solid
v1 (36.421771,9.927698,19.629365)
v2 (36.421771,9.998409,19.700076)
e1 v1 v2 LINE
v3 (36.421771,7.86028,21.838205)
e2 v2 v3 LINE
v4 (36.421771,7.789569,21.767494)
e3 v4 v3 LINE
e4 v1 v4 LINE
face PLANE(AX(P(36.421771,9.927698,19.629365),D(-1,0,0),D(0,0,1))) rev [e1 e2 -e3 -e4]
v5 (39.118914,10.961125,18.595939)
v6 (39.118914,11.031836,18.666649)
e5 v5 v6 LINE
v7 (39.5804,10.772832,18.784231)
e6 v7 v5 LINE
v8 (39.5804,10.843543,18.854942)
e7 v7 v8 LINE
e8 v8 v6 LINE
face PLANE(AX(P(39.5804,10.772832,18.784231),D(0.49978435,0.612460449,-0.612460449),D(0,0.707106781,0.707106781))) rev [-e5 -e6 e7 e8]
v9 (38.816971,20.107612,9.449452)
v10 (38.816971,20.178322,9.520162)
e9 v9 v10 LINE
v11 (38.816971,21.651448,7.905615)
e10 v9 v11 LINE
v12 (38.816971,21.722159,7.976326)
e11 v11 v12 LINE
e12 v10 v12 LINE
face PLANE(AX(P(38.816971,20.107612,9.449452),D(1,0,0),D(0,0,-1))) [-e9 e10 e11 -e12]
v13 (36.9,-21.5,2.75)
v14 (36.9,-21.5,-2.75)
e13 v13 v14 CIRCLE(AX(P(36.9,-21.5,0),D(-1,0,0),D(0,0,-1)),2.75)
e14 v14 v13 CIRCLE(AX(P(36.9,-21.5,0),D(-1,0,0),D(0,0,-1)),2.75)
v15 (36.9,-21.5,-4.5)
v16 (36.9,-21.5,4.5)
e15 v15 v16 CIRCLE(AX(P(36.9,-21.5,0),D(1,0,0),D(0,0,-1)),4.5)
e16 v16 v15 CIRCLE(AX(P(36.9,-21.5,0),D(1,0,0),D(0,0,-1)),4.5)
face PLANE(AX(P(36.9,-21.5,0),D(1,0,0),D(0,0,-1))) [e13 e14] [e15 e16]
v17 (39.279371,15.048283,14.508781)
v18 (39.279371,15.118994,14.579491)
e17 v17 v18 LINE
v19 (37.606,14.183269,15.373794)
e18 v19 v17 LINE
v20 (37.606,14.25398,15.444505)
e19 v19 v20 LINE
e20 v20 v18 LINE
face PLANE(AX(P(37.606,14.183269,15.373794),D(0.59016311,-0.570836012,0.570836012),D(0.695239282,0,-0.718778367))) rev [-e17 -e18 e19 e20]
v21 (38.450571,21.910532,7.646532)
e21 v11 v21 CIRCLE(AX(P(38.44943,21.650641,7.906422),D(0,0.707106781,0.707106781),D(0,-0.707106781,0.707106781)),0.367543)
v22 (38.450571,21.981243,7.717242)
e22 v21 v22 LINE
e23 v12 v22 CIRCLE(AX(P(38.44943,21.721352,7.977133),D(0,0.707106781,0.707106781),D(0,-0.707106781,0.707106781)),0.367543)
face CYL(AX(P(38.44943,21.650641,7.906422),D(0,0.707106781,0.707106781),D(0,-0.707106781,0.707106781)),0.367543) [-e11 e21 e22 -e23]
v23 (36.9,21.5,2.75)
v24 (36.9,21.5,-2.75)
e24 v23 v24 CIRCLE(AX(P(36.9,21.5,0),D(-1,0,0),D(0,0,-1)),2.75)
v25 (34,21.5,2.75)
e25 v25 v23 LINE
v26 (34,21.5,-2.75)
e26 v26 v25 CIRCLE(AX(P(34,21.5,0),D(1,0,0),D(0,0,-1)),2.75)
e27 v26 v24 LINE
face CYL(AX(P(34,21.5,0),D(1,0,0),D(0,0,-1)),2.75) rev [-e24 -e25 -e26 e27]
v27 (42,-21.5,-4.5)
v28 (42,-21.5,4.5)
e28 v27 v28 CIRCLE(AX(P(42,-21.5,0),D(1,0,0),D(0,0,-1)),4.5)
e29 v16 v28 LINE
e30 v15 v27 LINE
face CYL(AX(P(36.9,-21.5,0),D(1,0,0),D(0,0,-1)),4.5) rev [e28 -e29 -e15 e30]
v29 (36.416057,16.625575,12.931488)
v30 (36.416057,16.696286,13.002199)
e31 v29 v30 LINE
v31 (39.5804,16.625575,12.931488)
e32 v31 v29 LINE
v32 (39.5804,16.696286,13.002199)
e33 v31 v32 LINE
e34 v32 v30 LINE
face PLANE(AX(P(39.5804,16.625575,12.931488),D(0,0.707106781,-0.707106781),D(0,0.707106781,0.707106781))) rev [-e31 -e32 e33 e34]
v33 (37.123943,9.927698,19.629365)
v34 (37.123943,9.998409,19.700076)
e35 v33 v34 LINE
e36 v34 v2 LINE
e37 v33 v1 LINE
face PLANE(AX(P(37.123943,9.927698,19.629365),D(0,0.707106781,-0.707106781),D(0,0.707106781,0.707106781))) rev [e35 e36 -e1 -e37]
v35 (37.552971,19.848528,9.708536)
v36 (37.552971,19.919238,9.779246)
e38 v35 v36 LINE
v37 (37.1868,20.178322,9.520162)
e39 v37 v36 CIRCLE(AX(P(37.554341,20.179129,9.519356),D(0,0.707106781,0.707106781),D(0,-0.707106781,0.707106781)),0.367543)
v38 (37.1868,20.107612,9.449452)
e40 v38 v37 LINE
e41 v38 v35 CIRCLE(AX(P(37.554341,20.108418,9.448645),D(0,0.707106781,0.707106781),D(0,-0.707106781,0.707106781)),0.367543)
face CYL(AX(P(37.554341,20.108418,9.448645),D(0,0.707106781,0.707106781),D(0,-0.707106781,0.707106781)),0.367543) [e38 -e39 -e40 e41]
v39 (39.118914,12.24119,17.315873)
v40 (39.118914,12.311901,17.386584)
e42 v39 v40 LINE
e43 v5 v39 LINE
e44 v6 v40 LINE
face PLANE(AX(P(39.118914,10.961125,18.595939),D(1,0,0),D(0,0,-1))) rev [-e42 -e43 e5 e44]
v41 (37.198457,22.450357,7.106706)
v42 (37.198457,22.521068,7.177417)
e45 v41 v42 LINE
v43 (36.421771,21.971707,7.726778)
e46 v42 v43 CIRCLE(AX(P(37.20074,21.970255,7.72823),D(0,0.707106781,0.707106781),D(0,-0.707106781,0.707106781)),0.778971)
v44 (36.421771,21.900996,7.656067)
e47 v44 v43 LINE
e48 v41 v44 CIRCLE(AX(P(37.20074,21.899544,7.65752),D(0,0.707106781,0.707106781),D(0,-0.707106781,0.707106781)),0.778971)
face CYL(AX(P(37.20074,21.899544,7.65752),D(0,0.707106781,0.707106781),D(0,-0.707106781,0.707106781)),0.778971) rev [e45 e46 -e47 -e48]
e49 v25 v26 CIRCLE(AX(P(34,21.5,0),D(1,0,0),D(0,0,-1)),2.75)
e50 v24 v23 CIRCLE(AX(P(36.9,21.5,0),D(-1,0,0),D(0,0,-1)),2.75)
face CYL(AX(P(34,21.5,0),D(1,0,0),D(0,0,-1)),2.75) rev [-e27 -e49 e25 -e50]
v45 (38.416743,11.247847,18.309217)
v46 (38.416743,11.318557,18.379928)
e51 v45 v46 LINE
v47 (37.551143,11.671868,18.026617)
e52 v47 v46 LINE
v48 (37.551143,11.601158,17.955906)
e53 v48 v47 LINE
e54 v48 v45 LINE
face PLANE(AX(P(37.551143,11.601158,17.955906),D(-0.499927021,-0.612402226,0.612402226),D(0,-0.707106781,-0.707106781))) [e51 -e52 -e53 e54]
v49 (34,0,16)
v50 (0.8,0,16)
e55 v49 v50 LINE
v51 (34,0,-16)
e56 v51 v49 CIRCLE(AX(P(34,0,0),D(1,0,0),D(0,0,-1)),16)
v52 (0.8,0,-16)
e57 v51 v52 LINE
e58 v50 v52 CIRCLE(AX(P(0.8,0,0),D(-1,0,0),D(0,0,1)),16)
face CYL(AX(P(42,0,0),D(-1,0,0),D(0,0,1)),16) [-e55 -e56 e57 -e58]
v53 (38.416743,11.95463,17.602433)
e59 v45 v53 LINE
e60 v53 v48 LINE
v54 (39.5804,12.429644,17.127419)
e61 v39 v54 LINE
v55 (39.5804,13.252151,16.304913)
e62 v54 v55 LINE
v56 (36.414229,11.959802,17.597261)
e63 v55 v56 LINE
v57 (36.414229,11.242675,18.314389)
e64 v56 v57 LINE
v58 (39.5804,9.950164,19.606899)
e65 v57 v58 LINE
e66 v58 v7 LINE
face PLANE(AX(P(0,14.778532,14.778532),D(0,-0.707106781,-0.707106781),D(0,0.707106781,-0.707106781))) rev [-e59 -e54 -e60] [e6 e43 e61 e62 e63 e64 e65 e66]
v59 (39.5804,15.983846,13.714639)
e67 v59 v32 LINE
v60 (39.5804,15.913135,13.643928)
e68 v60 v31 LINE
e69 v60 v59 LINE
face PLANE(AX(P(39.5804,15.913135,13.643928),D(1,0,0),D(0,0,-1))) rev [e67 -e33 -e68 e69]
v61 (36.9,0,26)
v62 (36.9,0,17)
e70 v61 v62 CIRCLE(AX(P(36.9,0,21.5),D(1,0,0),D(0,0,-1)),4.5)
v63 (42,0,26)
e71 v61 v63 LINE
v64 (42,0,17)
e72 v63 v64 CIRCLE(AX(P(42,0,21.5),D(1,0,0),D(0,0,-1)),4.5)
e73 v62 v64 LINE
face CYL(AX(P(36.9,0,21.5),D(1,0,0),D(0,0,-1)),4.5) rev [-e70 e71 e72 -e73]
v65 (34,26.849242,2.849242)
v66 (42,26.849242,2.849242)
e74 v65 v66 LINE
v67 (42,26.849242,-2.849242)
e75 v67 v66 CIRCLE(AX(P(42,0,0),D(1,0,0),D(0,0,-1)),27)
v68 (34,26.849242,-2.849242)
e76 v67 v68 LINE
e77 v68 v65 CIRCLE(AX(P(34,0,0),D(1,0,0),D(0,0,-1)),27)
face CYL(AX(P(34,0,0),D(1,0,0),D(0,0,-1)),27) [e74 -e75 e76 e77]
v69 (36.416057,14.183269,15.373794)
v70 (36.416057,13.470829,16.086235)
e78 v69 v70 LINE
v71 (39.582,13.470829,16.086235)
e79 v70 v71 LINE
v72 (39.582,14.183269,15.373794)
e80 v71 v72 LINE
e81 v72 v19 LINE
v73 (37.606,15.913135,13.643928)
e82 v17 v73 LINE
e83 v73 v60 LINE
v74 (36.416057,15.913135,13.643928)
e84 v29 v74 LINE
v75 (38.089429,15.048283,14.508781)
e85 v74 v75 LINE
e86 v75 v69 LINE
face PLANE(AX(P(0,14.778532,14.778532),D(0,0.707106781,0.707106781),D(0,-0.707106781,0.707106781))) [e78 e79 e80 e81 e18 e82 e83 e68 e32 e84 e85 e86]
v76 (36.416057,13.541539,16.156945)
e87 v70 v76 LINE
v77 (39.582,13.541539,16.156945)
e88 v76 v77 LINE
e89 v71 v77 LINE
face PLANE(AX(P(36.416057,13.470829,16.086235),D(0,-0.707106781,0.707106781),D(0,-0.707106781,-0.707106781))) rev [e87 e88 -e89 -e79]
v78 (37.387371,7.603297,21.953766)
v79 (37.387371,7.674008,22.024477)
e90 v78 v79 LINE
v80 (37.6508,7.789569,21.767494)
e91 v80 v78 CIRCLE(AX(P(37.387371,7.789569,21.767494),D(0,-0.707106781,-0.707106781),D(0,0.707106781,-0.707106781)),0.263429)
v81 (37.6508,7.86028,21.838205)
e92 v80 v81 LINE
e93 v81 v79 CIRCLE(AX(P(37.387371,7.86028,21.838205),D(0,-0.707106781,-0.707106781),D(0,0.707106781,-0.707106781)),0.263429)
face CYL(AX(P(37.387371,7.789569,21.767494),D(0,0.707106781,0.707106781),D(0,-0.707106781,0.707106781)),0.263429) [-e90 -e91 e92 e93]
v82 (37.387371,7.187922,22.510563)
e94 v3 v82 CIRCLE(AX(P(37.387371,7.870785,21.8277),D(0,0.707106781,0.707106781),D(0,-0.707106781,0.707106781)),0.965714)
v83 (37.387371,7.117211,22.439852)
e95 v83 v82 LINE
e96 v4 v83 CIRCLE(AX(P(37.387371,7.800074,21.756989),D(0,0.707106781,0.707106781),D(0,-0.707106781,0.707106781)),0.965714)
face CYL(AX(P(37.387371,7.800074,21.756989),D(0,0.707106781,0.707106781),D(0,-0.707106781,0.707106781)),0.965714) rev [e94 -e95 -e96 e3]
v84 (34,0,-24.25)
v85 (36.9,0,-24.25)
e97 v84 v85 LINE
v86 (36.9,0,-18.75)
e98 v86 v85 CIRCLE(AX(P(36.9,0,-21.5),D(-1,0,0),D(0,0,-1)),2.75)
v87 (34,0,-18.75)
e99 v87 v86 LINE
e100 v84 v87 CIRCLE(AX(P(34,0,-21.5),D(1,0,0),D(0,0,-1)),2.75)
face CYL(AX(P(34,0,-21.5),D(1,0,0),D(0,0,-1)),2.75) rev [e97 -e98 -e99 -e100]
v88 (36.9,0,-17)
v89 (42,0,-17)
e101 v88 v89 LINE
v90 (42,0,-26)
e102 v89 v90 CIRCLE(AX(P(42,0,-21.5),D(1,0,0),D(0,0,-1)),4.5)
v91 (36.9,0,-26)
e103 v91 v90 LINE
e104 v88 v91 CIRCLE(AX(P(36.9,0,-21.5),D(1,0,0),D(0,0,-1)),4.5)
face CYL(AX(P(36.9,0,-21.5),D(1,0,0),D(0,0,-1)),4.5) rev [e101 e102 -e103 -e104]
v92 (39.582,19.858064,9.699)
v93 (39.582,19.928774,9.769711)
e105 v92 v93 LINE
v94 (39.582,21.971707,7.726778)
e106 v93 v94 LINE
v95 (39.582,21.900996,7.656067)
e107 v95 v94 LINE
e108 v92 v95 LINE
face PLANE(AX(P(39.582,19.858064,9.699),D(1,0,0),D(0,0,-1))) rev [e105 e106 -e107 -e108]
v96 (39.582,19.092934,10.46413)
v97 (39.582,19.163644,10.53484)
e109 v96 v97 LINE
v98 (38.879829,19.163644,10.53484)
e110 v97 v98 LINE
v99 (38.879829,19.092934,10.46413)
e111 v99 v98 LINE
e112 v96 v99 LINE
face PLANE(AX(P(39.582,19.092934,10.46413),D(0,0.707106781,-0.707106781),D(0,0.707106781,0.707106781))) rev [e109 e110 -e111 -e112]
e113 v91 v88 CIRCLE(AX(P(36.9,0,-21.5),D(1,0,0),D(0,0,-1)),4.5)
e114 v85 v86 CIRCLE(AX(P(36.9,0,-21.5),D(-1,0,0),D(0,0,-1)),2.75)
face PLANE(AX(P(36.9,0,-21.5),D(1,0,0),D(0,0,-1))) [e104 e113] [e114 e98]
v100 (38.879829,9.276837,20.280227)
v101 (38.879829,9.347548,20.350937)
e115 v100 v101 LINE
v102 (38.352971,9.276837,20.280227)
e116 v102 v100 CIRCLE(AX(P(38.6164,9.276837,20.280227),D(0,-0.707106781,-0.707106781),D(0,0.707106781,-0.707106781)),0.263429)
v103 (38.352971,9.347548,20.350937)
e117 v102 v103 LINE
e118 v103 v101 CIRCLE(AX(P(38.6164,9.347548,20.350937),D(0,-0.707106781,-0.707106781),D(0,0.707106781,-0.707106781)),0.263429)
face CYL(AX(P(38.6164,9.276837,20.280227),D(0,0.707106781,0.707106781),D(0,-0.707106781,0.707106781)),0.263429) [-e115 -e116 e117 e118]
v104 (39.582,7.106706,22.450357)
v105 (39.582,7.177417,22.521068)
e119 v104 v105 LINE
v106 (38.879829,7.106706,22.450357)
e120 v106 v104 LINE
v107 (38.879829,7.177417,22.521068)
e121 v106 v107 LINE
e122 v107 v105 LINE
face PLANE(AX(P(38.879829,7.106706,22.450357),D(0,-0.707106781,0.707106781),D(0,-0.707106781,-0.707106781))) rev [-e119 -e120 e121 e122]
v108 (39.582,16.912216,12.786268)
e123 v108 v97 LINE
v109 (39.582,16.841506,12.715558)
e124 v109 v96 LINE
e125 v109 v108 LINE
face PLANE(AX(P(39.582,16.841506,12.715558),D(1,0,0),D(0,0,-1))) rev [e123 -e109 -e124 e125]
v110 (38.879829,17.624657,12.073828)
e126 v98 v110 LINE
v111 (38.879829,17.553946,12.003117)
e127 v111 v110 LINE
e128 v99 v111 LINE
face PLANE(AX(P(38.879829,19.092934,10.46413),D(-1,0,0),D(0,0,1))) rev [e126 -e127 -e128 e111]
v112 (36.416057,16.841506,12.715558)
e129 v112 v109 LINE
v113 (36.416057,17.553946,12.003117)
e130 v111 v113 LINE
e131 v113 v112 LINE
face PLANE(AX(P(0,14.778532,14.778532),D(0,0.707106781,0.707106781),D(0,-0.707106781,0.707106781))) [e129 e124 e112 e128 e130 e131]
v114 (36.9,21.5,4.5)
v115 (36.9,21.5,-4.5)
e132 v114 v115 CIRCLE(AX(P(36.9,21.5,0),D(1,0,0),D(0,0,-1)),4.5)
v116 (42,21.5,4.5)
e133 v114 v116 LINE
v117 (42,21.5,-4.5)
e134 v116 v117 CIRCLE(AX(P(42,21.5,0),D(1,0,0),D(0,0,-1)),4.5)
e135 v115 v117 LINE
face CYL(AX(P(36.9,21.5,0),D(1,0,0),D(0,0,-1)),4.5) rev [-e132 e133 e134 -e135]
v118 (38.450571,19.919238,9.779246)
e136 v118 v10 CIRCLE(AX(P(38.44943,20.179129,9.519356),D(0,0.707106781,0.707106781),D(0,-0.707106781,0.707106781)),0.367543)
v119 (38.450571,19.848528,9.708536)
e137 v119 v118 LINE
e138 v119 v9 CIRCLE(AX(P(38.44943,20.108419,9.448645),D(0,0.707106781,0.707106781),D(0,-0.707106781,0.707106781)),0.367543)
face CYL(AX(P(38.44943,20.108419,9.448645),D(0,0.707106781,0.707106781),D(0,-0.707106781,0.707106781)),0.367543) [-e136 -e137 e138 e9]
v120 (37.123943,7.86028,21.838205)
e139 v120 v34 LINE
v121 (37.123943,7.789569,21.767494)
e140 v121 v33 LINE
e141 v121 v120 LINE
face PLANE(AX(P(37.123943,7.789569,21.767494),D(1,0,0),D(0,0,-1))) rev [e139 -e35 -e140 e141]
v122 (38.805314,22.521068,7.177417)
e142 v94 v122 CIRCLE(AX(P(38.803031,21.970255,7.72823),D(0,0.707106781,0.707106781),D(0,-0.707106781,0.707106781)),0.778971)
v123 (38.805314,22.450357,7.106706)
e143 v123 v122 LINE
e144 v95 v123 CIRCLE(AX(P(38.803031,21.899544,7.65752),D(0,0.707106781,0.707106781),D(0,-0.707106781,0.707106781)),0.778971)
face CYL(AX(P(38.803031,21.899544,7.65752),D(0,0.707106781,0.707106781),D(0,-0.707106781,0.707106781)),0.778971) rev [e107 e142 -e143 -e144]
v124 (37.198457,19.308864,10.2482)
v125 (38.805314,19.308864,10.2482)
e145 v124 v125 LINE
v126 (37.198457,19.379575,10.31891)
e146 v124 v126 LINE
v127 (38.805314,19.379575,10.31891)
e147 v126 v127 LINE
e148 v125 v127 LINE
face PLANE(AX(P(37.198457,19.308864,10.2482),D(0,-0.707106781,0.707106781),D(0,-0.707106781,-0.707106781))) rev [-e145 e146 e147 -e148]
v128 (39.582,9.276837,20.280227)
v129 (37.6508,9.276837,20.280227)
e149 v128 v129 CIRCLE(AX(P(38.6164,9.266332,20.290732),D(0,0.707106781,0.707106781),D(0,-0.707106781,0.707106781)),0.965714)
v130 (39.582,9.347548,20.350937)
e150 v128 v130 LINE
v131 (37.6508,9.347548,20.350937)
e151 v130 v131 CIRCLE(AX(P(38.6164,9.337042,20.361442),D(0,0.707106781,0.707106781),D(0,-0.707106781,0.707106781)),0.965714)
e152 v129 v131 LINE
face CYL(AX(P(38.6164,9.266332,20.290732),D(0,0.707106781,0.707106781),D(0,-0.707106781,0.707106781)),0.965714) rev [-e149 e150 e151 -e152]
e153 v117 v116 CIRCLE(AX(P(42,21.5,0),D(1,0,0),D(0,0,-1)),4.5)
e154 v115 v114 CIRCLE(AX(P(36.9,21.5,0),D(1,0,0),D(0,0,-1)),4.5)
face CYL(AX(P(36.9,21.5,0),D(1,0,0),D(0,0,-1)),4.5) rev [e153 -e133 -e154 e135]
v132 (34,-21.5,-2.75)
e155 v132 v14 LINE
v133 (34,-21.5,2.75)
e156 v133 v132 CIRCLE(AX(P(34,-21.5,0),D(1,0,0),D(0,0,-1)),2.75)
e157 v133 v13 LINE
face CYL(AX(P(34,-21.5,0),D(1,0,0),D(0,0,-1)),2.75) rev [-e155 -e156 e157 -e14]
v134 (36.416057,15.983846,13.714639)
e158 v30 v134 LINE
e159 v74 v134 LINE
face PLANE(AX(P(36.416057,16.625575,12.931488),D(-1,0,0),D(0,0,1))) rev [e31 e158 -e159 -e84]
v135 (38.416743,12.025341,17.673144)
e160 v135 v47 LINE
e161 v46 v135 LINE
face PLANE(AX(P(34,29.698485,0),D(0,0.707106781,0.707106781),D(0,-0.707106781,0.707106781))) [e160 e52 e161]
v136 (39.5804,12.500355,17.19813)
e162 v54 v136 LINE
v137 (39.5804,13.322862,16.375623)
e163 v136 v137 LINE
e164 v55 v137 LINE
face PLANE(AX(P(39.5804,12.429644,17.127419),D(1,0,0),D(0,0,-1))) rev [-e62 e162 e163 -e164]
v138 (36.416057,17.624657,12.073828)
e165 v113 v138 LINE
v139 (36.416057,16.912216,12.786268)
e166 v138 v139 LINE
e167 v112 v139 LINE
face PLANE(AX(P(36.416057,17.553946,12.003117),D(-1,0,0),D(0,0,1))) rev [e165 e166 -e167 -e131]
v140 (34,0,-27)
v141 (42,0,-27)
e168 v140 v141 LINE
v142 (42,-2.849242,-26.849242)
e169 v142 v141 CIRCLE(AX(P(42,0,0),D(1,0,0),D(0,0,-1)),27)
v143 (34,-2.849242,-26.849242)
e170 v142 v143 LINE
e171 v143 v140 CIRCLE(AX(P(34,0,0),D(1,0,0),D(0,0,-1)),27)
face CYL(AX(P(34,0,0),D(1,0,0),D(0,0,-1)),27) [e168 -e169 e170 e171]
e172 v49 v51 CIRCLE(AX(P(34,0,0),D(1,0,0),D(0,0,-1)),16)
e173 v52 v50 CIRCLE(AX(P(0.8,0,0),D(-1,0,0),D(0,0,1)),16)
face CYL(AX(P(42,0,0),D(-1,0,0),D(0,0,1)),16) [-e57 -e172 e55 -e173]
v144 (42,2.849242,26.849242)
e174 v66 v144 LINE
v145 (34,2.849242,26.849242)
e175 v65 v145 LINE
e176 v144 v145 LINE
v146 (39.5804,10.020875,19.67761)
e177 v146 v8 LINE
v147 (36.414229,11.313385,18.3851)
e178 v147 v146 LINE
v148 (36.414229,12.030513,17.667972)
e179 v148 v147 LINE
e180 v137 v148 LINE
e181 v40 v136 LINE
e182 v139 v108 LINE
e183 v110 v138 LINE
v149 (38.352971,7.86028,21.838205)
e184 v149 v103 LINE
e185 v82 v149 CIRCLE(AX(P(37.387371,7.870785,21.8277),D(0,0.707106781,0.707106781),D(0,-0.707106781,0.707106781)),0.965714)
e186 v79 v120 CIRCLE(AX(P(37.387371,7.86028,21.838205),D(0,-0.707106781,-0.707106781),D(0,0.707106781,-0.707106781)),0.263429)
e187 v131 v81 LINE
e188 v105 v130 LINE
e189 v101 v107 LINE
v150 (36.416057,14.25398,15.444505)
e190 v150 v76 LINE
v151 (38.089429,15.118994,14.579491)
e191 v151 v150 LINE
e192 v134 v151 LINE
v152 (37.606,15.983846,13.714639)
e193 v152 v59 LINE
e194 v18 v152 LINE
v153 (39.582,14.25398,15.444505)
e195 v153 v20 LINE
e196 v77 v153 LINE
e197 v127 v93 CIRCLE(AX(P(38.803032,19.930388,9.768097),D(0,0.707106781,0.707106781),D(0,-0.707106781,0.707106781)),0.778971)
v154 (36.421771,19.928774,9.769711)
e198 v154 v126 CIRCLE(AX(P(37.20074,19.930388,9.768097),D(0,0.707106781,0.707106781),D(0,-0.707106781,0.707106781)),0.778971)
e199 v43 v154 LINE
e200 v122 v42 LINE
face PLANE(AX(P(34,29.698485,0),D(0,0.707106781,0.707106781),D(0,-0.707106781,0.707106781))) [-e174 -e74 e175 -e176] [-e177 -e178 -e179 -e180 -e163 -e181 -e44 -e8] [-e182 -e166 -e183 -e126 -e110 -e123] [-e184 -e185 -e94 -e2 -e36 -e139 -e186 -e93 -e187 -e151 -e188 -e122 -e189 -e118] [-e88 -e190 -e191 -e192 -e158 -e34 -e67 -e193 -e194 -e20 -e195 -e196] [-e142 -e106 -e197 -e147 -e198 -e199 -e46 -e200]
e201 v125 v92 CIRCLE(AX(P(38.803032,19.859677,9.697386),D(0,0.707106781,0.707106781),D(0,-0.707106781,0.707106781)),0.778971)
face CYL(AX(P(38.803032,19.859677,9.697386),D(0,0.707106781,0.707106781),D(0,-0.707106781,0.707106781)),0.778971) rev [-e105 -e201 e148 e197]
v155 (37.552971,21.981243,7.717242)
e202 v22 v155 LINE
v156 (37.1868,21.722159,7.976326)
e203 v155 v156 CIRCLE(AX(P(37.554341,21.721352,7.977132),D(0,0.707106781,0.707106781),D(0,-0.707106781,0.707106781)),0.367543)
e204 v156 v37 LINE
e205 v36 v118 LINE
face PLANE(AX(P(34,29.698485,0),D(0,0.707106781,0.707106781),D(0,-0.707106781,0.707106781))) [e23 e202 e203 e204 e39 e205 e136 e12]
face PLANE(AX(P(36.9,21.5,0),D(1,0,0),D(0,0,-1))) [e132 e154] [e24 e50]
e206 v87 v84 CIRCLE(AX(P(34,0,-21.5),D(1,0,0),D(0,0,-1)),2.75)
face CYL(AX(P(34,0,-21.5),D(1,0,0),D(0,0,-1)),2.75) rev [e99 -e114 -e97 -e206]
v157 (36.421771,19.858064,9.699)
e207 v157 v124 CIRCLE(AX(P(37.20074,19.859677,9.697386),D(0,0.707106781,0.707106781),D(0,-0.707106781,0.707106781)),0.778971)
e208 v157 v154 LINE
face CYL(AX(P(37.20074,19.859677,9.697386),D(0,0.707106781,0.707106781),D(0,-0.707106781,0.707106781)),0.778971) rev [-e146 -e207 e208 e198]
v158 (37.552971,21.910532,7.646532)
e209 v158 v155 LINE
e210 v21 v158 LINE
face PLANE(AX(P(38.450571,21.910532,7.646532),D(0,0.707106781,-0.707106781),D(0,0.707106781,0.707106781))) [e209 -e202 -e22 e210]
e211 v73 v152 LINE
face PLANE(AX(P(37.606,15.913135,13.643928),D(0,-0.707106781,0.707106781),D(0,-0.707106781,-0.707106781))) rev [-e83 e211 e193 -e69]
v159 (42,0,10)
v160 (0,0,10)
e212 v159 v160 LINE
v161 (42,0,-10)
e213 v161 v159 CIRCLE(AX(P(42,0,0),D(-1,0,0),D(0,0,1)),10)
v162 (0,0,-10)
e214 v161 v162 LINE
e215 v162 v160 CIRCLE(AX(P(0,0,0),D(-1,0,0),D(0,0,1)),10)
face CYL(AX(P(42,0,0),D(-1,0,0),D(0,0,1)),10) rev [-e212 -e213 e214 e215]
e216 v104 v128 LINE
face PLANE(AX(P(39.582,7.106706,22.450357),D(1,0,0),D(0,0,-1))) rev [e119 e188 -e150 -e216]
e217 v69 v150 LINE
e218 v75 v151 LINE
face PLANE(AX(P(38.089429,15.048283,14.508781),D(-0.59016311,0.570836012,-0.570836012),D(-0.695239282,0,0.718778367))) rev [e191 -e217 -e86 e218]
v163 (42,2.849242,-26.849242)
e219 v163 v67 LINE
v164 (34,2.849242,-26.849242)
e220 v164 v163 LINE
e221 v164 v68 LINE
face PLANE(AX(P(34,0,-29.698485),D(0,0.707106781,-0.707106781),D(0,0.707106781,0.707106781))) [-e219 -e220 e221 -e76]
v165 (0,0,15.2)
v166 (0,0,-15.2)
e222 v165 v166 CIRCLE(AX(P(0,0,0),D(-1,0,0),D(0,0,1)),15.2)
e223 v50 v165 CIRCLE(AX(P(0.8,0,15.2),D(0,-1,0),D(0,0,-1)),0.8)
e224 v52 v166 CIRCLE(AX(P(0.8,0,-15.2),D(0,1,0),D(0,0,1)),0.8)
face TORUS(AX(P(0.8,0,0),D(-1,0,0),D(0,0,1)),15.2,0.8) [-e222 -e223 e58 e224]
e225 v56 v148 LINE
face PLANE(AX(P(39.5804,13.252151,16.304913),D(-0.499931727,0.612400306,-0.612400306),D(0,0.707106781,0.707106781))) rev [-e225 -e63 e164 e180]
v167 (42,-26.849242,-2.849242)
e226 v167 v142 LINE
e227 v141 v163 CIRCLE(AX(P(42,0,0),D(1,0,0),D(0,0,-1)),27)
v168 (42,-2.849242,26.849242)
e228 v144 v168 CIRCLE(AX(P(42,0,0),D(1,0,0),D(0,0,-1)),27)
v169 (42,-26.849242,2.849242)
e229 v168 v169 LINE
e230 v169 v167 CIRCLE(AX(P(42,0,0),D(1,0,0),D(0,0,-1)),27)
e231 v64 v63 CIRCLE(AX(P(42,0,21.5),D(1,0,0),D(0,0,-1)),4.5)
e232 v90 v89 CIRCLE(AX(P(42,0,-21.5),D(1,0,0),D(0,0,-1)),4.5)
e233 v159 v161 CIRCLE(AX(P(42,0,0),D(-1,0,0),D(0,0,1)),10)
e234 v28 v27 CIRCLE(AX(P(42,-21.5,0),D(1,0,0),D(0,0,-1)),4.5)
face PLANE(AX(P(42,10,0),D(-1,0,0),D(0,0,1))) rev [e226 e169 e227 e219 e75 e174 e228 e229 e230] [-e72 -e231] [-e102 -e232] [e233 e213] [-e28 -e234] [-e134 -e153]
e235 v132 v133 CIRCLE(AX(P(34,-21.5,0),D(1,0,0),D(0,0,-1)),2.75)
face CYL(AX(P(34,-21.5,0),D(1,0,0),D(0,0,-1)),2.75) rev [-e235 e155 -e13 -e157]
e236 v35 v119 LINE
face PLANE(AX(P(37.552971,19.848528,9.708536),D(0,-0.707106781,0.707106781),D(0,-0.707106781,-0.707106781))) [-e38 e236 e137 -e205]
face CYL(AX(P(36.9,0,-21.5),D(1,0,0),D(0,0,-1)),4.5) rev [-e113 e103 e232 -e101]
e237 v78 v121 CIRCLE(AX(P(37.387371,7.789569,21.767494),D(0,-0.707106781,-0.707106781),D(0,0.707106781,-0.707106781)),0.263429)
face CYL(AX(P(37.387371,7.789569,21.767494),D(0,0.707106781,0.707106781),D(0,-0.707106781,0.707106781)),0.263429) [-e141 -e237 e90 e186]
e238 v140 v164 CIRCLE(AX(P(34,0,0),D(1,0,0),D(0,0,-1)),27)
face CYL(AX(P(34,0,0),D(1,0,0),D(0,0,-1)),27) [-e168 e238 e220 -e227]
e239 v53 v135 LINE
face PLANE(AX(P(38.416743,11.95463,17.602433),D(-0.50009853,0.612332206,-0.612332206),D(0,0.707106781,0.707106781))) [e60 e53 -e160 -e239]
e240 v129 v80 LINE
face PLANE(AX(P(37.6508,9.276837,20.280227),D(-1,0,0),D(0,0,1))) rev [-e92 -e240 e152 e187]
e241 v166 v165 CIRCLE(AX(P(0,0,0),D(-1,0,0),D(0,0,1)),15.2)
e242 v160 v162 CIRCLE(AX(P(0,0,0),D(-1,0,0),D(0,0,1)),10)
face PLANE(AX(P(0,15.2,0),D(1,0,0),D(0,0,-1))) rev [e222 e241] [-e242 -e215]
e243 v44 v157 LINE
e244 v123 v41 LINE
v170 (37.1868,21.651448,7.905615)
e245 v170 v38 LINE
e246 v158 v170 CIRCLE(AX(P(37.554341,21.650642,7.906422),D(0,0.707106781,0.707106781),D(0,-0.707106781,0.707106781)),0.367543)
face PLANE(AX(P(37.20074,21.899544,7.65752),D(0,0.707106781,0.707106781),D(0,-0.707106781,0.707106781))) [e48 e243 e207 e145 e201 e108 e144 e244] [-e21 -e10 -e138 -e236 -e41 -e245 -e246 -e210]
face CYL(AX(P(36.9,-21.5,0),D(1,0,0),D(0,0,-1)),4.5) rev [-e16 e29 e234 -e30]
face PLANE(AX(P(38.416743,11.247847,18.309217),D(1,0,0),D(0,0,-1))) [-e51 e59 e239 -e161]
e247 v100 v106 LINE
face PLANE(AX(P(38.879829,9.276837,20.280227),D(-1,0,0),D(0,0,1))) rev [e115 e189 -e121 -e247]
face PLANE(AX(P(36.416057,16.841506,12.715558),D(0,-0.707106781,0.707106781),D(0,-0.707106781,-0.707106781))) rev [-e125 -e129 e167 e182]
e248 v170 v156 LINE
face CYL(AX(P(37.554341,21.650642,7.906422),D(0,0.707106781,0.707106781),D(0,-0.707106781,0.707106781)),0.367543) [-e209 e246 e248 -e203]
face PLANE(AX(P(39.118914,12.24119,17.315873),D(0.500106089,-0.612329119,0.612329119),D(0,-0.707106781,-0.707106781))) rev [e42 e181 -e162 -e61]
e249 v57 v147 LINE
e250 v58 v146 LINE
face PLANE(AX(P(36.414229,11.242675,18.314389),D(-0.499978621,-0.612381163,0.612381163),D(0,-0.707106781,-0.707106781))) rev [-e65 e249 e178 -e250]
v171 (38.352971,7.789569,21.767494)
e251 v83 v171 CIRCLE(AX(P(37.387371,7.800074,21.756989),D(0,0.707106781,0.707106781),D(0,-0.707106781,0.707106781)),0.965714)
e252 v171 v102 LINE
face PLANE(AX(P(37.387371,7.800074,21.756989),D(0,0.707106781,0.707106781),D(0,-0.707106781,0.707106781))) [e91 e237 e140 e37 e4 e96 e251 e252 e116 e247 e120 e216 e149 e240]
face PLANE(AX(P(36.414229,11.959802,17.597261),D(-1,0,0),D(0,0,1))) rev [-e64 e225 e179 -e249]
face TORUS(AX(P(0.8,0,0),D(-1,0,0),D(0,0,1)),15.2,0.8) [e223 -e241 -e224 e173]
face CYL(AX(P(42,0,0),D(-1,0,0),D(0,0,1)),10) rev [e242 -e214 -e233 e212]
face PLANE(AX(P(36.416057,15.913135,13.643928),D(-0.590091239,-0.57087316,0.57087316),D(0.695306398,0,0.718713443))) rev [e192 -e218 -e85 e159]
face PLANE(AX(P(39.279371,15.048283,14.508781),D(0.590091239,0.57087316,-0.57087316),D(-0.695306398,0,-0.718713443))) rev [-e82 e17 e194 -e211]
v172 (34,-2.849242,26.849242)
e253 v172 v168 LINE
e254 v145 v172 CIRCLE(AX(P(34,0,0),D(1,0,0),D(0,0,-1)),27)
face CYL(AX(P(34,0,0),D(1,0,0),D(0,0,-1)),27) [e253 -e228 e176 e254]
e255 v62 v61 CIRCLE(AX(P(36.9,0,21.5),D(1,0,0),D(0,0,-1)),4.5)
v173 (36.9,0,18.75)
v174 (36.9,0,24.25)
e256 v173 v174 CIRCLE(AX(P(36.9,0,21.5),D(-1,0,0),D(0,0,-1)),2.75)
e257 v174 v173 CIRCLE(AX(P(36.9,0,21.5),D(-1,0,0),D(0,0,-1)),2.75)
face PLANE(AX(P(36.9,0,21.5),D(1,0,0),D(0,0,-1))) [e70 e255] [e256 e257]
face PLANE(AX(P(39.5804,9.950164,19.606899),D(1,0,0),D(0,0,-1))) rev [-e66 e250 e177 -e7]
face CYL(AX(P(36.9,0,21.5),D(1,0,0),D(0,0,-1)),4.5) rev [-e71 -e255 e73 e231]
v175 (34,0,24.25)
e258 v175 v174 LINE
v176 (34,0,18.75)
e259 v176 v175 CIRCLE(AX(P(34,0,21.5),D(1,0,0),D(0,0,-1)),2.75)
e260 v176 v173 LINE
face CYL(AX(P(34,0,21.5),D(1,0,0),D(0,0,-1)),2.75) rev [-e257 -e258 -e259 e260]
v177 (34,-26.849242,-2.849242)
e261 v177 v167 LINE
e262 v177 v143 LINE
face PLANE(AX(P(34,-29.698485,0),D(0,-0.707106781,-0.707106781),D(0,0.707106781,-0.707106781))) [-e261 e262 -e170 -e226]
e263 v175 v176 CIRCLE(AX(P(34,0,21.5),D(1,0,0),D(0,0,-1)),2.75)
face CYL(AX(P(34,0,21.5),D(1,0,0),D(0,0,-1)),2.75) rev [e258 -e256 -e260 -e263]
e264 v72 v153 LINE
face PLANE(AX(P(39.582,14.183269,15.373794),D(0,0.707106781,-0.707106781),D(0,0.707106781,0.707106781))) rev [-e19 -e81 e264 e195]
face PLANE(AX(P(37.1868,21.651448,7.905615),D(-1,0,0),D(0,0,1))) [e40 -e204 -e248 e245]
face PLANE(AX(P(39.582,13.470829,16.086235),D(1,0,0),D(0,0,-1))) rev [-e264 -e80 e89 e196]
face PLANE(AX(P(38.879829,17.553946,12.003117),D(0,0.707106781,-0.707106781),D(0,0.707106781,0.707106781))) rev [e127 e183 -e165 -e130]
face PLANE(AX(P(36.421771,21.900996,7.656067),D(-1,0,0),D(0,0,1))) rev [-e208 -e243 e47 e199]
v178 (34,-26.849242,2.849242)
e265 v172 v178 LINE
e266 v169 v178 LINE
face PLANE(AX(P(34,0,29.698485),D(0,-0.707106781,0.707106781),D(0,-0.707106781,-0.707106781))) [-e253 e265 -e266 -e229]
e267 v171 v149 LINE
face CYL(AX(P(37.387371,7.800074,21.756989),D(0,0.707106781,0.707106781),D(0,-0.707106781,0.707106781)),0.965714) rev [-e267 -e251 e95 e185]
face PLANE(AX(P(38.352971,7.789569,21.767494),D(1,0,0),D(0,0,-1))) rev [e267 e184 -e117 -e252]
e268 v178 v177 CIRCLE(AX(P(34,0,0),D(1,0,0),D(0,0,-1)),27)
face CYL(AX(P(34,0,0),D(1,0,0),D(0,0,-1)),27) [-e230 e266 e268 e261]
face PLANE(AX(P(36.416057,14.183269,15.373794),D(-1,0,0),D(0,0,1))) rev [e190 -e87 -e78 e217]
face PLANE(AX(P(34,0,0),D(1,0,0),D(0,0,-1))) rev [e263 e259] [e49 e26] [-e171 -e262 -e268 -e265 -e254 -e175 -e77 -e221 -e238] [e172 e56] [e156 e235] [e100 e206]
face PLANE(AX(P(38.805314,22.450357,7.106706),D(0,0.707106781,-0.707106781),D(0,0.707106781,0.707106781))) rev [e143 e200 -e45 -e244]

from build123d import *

# Parameters (mm, degrees)
SKETCH2_R            = 27
SKETCH2_R_2          = 2.75
SKETCH2_R_3          = 10
BOSS_EXTRUDE1_DEPTH  = 8
SKETCH3_R            = 4.5
CUT_EXTRUDE1_DEPTH   = 5.1
LPATTERN1_COUNT      = 2
LPATTERN1_PITCH      = 30.405591591
LPATTERN1_COUNT_DIR2 = 2
LPATTERN1_PITCH_DIR2 = 30.405591591
SKETCH5_R            = 54
CUT_EXTRUDE2_DEPTH   = 8
CUT_EXTRUDE3_DEPTH   = 0.1
CUT_EXTRUDE4_DEPTH   = 0.1
CUT_EXTRUDE5_DEPTH   = 0.1
CUT_EXTRUDE6_DEPTH   = 0.1
CUT_EXTRUDE7_DEPTH   = 0.1


with BuildPart() as part:
    # Sketch1 → Revolve1 (revolve)
    with BuildSketch(Plane.XY, mode=Mode.PRIVATE) as revolve1_sk:
        with BuildLine():
            Line((0, 10), (42, 10))
            Line((42, 10), (42, 15.2))
            ThreePointArc((42, 15.2), (41.765685425, 15.765685425), (41.2, 16))
            Line((41.2, 16), (0.8, 16))
            ThreePointArc((0.8, 16), (0.234314575, 15.765685425), (0, 15.2))
            Line((0, 15.2), (0, 10))
        make_face()
    revolve(revolve1_sk.sketch.rotate(Axis((42, 0, 0), (-1, 0, 0)), 270), axis=Axis((42, 0, 0), (-1, 0, 0)))

    # Sketch2 → Boss-Extrude1 (add)
    with BuildSketch(Plane(origin=(42, 0, 0), x_dir=(0, 0, -1), z_dir=(1, 0, 0))):
        Circle(SKETCH2_R)
        with Locations((21.5, 0)):
            Circle(SKETCH2_R_2, mode=Mode.SUBTRACT)
        with Locations((0, 21.5)):
            Circle(SKETCH2_R_2, mode=Mode.SUBTRACT)
        with Locations((0, -21.5)):
            Circle(SKETCH2_R_2, mode=Mode.SUBTRACT)
        with Locations(Location((0, 0, 0), (0, 0, 180))):
            Circle(SKETCH2_R_3, mode=Mode.SUBTRACT)
        with Locations((-21.5, 0)):
            Circle(SKETCH2_R_2, mode=Mode.SUBTRACT)
    extrude(amount=-BOSS_EXTRUDE1_DEPTH)

    # Sketch3 → Cut-Extrude1 (cut)
    with BuildSketch(Plane(origin=(42, 0, 0), x_dir=(0, 0, -1), z_dir=(1, 0, 0))):
        with Locations((0, 21.5)):
            Circle(SKETCH3_R)
    cut_extrude1 = extrude(amount=-CUT_EXTRUDE1_DEPTH, mode=Mode.SUBTRACT)

    # LPattern1: Cut-Extrude1 2 × 2
    with Locations(*[Vector(0, -0.7071067811865475, 0.7071067811865477) * (i * LPATTERN1_PITCH) + Vector(0, -0.7071067811865477, -0.7071067811865474) * (j * LPATTERN1_PITCH_DIR2) for i in range(LPATTERN1_COUNT) for j in range(LPATTERN1_COUNT_DIR2) if (i, j) != (0, 0)]):
        add(cut_extrude1, mode=Mode.SUBTRACT)

    # Sketch5 → Cut-Extrude2 (cut)
    with BuildSketch(Plane(origin=(42, 0, 0), x_dir=(0, 0, -1), z_dir=(1, 0, 0))):
        Circle(SKETCH5_R)
        Polygon((-29.69848481, 0), (0, -29.69848481), (29.69848481, 0), (0, 29.69848481), align=None, mode=Mode.SUBTRACT)
    extrude(amount=-CUT_EXTRUDE2_DEPTH, mode=Mode.SUBTRACT)

    # Sketch6 → Cut-Extrude3 (cut)
    with BuildSketch(Plane(origin=(0, 14.849242405, 14.849242405), x_dir=(1, 0, 0), z_dir=(0, 0.7071067811865477, 0.7071067811865475))):
        with BuildLine():
            Line((38.352971429, -9.883885714), (38.352971429, -7.780571429))
            ThreePointArc((38.352971429, -7.780571429), (38.6164, -7.517142857), (38.879828571, -7.780571429))
            Line((38.879828571, -7.780571429), (38.879828571, -10.8496))
            Line((38.879828571, -10.8496), (39.582, -10.8496))
            Line((39.582, -10.8496), (39.582, -7.780571429))
            ThreePointArc((39.582, -7.780571429), (38.6164, -6.829713846), (37.6508, -7.780571429))
            Line((37.6508, -7.780571429), (37.6508, -9.883885714))
            ThreePointArc((37.6508, -9.883885714), (37.387371429, -10.147314286), (37.123942857, -9.883885714))
            Line((37.123942857, -9.883885714), (37.123942857, -6.860114286))
            Line((37.123942857, -6.860114286), (36.421771429, -6.860114286))
            Line((36.421771429, -6.860114286), (36.421771429, -9.883885714))
            ThreePointArc((36.421771429, -9.883885714), (37.387371429, -10.834743297), (38.352971429, -9.883885714))
        make_face()
    extrude(amount=-CUT_EXTRUDE3_DEPTH, mode=Mode.SUBTRACT)

    # Sketch7 → Cut-Extrude4 (cut)
    with BuildSketch(Plane(origin=(0, 14.849242405, 14.849242405), x_dir=(1, 0, 0), z_dir=(0, 0.7071067811865477, 0.7071067811865475))):
        Polygon((36.414228571, -5.000457143), (39.5804, -6.828342857), (39.5804, -5.664914286), (39.118914286, -5.398628571), (39.118914286, -3.588342857), (39.5804, -3.321828571), (39.5804, -2.158628571), (36.414228571, -3.986285714), align=None)
        Polygon((37.551142857, -4.493485714), (38.416742857, -4.993142857), (38.416742857, -3.9936), align=None, mode=Mode.SUBTRACT)
    extrude(amount=-CUT_EXTRUDE4_DEPTH, mode=Mode.SUBTRACT)

    # Sketch8 → Cut-Extrude5 (cut)
    with BuildSketch(Plane(origin=(0, 14.849242405, 14.849242405), x_dir=(1, 0, 0), z_dir=(0, 0.7071067811865477, 0.7071067811865475))):
        Polygon((36.416057143, 2.612114286), (36.416057143, 1.604571429), (38.089428571, 0.381485714), (36.416057143, -0.841828571), (36.416057143, -1.849371429), (39.582, -1.849371429), (39.582, -0.841828571), (37.606, -0.841828571), (39.279371429, 0.381485714), (37.606, 1.604571429), (39.5804, 1.604571429), (39.5804, 2.612114286), align=None)
    extrude(amount=-CUT_EXTRUDE5_DEPTH, mode=Mode.SUBTRACT)

    # Sketch9 → Cut-Extrude6 (cut)
    with BuildSketch(Plane(origin=(0, 14.849242405, 14.849242405), x_dir=(1, 0, 0), z_dir=(0, 0.7071067811865477, 0.7071067811865475))):
        Polygon((36.416057143, 2.917485714), (39.582, 2.917485714), (39.582, 6.101485714), (38.879828571, 6.101485714), (38.879828571, 3.925028571), (36.416057143, 3.925028571), align=None)
    extrude(amount=-CUT_EXTRUDE6_DEPTH, mode=Mode.SUBTRACT)

    # Sketch10 → Cut-Extrude7 (cut)
    with BuildSketch(Plane(origin=(0, 14.849242405, 14.849242405), x_dir=(1, 0, 0), z_dir=(0, 0.7071067811865477, 0.7071067811865475))):
        with BuildLine():
            Line((36.421771429, 10.072685714), (36.421771429, 7.183542857))
            ThreePointArc((36.421771429, 7.183542857), (36.649923534, 6.635009248), (37.198457143, 6.406857143))
            Line((37.198457143, 6.406857143), (38.805314286, 6.406857143))
            ThreePointArc((38.805314286, 6.406857143), (39.353847895, 6.635009248), (39.582, 7.183542857))
            Line((39.582, 7.183542857), (39.582, 10.072685714))
            ThreePointArc((39.582, 10.072685714), (39.353928291, 10.621366852), (38.805314286, 10.8496))
            Line((38.805314286, 10.8496), (37.198457143, 10.8496))
            ThreePointArc((37.198457143, 10.8496), (36.649843138, 10.621366852), (36.421771429, 10.072685714))
        make_face()
        with BuildLine():
            Line((37.552971429, 7.170057143), (38.450571429, 7.170057143))
            ThreePointArc((38.450571429, 7.170057143), (38.709322389, 7.277706182), (38.816971429, 7.536457143))
            Line((38.816971429, 7.536457143), (38.816971429, 9.719771429))
            ThreePointArc((38.816971429, 9.719771429), (38.709322389, 9.978522389), (38.450571429, 10.086171429))
            Line((38.450571429, 10.086171429), (37.552971429, 10.086171429))
            ThreePointArc((37.552971429, 10.086171429), (37.294367965, 9.978442068), (37.1868, 9.719771429))
            Line((37.1868, 9.719771429), (37.1868, 7.536457143))
            ThreePointArc((37.1868, 7.536457143), (37.294367965, 7.277786503), (37.552971429, 7.170057143))
        make_face(mode=Mode.SUBTRACT)
    extrude(amount=-CUT_EXTRUDE7_DEPTH, mode=Mode.SUBTRACT)


solid = part.part
